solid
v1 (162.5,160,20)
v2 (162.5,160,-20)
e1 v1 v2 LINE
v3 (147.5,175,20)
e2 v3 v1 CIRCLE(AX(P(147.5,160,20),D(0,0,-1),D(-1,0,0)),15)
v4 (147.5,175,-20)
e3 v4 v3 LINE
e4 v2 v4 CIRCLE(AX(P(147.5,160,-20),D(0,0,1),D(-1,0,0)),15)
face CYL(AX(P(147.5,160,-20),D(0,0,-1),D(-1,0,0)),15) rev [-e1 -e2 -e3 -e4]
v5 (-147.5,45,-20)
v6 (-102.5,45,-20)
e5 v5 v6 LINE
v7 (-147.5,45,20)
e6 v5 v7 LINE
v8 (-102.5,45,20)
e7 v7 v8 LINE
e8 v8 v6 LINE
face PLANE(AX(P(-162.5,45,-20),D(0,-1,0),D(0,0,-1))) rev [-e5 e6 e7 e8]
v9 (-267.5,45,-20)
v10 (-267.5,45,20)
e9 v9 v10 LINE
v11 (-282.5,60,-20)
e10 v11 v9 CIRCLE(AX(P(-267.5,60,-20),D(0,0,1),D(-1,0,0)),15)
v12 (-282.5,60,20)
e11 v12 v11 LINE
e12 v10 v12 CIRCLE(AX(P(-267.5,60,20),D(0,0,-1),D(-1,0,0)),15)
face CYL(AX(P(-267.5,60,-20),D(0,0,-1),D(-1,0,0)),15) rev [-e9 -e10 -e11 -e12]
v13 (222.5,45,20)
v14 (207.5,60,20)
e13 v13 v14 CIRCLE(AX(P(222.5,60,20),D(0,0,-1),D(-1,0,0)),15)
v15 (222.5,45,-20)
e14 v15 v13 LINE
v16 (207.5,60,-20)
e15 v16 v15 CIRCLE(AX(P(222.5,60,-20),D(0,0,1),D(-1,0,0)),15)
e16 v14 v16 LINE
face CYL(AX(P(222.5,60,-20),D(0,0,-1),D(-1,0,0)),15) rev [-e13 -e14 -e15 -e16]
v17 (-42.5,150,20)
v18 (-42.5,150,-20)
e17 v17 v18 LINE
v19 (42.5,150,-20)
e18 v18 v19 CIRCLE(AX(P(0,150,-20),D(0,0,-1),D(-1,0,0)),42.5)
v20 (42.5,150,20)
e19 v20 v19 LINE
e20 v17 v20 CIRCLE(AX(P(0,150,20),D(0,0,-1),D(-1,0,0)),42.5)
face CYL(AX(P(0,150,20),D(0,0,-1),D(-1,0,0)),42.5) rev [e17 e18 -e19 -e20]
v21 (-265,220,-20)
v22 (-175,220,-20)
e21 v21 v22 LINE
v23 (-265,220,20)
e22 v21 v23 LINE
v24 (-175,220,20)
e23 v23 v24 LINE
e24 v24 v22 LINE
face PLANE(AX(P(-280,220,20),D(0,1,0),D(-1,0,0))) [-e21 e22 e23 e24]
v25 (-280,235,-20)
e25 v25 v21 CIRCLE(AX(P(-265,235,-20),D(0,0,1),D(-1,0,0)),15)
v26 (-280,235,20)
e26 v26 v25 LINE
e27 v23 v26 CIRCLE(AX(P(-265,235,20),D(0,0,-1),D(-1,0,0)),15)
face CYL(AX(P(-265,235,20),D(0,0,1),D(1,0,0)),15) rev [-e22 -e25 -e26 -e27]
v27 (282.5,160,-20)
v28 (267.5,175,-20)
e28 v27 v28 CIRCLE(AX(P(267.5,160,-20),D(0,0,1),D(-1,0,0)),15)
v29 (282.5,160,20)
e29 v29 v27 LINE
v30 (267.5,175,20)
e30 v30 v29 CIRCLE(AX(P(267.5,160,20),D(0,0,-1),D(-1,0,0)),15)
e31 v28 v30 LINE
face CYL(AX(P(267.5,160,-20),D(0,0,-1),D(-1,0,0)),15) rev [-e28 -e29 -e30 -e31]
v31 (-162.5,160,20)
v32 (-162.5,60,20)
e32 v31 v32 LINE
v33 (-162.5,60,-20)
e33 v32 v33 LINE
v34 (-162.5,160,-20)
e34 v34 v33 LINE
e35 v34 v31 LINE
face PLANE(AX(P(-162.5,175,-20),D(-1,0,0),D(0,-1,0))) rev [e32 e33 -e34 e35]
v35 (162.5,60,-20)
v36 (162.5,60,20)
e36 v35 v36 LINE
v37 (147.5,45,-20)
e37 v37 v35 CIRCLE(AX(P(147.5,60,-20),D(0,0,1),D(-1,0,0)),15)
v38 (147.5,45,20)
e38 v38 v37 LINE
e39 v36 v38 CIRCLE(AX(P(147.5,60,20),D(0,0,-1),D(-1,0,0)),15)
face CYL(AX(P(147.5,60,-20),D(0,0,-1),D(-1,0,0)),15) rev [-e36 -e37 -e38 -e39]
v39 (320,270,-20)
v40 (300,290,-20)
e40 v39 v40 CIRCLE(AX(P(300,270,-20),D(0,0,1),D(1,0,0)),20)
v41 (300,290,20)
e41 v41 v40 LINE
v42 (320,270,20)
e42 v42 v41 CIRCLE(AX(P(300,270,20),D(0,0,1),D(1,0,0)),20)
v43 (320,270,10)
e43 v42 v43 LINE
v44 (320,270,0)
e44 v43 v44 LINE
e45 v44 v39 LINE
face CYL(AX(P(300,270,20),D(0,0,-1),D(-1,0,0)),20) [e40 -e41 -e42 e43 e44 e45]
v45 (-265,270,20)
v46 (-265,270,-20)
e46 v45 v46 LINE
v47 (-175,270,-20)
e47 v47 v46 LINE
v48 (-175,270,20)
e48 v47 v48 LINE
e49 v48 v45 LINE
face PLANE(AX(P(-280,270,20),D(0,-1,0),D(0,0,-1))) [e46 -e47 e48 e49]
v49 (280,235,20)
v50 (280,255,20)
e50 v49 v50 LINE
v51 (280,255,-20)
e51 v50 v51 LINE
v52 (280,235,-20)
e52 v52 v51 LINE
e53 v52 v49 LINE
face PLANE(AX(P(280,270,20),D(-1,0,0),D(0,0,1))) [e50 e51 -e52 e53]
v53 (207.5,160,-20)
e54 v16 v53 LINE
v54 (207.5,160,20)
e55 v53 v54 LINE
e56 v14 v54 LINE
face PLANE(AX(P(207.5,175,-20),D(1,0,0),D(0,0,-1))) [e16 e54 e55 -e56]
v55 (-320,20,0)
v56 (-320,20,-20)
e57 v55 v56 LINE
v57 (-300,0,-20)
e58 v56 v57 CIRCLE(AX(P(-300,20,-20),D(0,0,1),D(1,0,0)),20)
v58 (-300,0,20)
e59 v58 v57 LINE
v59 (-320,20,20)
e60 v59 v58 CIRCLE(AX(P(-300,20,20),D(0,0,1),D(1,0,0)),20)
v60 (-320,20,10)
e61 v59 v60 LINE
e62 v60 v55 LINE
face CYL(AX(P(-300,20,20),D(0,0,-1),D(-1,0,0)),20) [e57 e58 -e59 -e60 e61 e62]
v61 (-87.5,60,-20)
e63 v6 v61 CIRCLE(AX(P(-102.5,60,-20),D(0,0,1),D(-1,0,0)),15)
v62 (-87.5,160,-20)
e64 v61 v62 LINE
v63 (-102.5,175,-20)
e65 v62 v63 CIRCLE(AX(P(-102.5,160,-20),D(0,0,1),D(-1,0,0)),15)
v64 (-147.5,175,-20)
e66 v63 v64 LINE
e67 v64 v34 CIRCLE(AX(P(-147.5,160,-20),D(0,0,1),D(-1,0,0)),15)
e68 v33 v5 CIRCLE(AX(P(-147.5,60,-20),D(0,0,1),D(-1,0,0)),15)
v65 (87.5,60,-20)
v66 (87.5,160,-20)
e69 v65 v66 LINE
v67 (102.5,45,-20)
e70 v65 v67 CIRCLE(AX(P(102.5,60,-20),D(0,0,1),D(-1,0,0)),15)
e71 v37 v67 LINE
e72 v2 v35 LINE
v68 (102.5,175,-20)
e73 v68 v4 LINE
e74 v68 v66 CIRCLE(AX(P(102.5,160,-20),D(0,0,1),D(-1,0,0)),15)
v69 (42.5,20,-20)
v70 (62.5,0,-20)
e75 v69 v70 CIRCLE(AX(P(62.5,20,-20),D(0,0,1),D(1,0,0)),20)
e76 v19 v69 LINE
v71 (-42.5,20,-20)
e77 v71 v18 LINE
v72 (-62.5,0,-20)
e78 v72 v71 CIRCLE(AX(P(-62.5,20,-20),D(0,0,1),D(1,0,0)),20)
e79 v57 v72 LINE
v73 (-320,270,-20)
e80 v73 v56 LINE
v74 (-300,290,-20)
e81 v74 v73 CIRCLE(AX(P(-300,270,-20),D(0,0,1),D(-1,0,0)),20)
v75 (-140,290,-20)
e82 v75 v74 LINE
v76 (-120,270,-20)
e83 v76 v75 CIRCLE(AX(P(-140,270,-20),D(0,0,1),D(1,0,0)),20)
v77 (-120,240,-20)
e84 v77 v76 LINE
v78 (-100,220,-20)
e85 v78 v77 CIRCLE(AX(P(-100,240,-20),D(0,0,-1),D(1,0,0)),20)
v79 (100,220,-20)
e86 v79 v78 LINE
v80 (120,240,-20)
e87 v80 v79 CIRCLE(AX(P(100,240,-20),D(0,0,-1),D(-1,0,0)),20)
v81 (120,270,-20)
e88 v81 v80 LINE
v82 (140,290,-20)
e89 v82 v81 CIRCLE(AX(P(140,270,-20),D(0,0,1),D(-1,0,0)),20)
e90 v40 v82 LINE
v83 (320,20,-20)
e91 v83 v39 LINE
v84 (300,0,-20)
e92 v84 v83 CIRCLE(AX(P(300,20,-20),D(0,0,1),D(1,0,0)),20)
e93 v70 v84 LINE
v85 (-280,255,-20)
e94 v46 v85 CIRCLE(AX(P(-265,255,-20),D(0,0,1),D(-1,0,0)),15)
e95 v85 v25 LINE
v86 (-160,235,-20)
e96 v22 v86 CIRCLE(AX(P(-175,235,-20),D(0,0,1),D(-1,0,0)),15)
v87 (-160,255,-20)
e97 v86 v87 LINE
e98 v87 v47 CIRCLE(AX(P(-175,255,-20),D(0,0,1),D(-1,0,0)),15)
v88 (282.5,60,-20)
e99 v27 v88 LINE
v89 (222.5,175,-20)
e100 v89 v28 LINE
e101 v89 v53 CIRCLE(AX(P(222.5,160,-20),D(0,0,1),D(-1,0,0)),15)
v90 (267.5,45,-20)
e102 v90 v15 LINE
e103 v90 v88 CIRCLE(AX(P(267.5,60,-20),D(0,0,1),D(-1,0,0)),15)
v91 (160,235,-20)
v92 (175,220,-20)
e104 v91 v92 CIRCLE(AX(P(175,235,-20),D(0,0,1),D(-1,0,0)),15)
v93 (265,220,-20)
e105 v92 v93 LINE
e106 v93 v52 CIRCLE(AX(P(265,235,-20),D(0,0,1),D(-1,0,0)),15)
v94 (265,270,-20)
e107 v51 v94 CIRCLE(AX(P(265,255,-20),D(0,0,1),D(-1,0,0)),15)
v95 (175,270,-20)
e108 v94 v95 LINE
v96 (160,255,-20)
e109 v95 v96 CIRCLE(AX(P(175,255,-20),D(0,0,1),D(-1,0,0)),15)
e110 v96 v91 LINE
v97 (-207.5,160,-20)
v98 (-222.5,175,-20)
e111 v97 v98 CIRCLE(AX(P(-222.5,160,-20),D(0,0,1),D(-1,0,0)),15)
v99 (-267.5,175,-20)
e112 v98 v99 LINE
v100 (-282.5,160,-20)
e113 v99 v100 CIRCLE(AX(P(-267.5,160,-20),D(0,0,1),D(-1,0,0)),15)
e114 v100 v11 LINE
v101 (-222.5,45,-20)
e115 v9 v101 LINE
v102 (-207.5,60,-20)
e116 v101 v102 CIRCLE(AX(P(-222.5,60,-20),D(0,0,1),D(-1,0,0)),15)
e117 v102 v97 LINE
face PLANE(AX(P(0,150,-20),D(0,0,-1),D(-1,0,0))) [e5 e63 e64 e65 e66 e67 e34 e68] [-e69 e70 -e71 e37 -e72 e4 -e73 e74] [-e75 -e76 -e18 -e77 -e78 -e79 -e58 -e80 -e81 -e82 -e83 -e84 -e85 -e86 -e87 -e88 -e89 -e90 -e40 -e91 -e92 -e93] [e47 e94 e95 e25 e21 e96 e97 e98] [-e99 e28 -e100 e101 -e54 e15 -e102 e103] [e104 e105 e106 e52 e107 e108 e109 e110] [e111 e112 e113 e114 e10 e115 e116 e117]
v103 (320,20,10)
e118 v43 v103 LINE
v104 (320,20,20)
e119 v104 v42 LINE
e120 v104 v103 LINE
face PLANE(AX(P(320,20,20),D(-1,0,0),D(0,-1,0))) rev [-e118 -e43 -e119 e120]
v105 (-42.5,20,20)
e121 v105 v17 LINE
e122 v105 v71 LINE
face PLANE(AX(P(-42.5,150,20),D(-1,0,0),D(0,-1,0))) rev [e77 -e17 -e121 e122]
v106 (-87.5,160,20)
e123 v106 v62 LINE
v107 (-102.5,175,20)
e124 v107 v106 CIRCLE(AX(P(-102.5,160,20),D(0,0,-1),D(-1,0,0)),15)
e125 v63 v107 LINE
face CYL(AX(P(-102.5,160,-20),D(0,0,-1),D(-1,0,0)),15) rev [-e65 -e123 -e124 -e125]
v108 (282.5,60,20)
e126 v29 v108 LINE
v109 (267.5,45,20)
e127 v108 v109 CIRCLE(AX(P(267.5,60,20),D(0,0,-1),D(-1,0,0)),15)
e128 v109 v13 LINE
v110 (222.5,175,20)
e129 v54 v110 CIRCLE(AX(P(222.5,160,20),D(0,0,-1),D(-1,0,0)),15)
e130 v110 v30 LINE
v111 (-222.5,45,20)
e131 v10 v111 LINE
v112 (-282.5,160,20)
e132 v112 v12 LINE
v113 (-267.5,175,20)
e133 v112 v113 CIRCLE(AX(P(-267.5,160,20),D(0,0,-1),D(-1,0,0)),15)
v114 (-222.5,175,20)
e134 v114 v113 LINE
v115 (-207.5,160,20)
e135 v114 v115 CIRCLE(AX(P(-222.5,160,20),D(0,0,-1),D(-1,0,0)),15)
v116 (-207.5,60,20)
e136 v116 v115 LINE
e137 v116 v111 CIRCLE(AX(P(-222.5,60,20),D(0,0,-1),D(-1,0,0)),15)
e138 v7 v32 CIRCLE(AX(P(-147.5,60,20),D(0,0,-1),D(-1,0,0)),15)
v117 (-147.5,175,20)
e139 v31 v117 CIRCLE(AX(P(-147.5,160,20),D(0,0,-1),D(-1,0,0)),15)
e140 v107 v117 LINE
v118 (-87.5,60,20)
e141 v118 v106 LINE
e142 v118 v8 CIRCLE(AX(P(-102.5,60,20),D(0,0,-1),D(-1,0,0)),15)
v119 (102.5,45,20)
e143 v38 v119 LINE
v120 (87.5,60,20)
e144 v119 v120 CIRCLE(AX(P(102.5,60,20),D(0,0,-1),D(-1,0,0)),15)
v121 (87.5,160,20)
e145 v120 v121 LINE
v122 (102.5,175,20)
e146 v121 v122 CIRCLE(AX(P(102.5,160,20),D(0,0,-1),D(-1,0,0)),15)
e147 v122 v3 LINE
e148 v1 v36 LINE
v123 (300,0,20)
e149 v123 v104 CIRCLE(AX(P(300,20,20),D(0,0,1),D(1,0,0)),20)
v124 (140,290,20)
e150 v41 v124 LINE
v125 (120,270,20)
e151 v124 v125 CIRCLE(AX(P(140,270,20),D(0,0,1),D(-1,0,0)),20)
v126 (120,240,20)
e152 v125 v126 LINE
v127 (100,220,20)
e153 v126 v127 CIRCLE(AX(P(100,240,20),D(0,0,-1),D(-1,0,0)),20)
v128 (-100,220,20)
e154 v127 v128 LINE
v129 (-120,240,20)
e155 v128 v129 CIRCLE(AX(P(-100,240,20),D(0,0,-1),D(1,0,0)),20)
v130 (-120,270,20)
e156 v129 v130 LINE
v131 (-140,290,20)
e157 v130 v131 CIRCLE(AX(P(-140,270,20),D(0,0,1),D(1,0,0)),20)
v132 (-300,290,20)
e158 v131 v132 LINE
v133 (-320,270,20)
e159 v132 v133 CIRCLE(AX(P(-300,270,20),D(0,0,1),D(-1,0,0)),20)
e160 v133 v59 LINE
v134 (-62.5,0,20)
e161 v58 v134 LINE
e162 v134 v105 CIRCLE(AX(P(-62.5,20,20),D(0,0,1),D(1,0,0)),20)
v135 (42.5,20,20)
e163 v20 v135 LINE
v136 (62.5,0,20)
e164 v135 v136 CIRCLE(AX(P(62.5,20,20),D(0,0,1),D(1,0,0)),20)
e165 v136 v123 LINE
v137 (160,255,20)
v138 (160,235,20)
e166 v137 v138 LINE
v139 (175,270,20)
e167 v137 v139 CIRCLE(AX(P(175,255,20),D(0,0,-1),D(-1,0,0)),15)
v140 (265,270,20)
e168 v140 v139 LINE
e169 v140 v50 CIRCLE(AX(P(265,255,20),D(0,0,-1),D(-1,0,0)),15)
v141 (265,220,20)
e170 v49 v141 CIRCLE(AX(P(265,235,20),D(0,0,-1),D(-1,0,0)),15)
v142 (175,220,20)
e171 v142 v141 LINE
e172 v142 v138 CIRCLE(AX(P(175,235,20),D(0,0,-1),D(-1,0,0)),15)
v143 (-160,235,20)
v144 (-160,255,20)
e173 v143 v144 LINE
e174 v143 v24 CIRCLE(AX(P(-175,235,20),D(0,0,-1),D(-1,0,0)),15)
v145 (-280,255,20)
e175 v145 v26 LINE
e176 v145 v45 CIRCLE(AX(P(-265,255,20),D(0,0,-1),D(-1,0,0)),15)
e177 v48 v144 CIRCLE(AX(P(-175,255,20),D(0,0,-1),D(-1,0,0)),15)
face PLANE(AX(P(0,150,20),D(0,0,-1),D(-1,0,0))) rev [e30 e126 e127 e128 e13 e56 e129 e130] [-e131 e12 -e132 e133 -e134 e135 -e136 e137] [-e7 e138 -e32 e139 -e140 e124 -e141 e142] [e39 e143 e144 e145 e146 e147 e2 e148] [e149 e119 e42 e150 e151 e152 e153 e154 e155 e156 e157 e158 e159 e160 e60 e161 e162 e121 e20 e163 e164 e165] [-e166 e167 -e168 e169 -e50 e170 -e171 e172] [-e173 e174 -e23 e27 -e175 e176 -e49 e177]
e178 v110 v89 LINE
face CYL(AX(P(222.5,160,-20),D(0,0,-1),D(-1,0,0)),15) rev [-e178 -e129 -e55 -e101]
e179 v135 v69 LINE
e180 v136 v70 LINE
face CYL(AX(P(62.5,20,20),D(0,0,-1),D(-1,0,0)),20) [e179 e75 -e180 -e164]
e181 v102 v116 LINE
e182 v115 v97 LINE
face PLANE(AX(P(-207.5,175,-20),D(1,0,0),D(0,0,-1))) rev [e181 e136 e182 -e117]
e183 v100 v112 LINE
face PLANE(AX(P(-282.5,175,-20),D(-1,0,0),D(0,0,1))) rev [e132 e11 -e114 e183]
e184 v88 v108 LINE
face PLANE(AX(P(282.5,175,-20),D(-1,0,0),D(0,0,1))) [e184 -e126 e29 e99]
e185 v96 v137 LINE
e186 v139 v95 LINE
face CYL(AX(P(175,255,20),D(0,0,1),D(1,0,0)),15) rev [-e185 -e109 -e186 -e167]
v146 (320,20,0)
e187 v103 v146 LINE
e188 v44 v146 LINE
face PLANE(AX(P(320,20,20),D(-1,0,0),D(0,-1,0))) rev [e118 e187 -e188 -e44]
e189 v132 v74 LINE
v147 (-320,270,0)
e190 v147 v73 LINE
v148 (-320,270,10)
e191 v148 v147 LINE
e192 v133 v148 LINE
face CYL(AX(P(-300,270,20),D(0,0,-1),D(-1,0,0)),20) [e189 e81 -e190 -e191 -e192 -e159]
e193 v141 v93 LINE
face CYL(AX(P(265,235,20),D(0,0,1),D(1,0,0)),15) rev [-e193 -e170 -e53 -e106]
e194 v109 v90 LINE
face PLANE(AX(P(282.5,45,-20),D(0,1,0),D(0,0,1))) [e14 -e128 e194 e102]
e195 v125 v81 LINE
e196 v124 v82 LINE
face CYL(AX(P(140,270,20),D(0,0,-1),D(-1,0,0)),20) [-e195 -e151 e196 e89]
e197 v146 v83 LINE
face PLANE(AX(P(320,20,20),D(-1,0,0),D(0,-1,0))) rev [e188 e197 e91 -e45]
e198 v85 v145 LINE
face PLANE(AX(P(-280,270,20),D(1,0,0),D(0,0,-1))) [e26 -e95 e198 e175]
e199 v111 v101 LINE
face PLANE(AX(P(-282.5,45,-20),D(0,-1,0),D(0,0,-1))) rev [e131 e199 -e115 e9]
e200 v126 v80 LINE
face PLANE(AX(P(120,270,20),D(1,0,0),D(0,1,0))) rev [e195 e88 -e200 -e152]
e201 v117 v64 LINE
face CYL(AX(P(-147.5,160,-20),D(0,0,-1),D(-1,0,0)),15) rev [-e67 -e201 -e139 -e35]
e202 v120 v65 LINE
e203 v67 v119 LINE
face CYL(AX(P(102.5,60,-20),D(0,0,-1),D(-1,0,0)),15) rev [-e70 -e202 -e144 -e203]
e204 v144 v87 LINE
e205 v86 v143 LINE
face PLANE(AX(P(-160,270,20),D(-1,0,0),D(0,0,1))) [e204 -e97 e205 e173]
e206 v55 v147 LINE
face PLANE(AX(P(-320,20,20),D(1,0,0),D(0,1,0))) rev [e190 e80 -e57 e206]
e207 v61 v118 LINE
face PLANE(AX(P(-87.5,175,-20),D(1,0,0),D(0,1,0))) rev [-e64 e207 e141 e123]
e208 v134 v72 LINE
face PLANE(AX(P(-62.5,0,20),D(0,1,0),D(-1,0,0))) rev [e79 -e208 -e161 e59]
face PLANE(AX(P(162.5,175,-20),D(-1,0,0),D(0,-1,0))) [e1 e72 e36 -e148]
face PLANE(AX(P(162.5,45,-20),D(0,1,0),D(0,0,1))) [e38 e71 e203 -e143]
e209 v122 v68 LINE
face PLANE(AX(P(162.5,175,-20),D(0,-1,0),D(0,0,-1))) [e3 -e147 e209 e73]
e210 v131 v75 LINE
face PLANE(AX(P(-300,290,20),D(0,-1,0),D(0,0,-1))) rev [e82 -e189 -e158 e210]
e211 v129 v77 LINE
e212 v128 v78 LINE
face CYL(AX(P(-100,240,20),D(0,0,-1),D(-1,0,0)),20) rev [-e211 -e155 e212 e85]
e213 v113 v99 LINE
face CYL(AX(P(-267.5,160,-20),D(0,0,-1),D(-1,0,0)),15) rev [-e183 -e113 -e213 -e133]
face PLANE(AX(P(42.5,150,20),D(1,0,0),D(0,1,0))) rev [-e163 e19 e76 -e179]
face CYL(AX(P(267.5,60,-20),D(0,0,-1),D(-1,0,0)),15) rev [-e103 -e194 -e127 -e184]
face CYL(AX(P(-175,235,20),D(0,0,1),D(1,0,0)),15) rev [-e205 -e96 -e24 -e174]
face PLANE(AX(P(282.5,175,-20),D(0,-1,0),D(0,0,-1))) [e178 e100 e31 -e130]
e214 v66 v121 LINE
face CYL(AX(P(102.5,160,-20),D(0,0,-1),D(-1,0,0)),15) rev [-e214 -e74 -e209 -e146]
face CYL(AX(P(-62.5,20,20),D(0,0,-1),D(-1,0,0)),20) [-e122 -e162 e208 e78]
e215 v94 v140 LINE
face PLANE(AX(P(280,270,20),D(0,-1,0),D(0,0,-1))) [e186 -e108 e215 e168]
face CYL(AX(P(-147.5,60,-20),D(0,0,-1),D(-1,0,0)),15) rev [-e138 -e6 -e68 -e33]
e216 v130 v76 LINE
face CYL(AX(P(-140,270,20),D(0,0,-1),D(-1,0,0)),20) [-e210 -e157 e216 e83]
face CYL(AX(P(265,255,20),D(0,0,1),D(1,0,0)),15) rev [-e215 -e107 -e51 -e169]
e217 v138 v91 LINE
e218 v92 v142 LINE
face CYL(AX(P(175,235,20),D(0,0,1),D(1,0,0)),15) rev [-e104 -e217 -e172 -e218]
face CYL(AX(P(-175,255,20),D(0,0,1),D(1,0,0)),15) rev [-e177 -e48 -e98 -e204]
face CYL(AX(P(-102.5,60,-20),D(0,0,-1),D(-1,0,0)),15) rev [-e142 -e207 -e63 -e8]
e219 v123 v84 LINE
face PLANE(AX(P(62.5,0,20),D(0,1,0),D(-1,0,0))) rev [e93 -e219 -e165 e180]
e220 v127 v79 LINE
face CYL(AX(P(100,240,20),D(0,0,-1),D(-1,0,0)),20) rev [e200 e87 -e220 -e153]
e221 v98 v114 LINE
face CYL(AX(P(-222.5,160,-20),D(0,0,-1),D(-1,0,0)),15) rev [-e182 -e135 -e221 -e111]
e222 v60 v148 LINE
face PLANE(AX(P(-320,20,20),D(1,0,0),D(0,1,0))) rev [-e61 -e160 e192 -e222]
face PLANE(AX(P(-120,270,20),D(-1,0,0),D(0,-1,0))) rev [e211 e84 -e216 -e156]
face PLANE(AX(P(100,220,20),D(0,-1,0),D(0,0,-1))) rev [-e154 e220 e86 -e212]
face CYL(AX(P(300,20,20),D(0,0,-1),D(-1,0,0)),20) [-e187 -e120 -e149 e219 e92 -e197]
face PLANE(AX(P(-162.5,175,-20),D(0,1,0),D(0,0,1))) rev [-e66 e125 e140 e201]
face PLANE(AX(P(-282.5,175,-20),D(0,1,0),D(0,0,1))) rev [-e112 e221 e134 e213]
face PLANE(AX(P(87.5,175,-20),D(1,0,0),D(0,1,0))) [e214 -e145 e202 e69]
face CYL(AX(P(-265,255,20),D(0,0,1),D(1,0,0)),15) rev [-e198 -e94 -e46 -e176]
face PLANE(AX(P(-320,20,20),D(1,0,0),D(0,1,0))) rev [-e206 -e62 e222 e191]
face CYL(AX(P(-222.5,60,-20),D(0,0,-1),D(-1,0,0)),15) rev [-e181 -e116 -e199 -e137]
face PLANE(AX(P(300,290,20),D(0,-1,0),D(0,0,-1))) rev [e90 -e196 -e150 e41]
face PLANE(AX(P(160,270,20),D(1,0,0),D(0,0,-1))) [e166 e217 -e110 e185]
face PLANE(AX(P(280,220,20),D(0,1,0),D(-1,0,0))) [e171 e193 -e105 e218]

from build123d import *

# Parameters (mm, degrees)
SKETCH1_W            = 120
SKETCH1_H            = 50
BOSS_EXTRUDE1_DEPTH  = 20
FILLET1_R            = 15
SKETCH2_W            = 75
SKETCH2_H            = 130
CUT_EXTRUDE1_DEPTH   = 433.319326424
FILLET2_R            = 15
FILLET2_OF_MIRROR1_R = 15


with BuildPart() as part:
    # Sketch1 → Boss-Extrude1 (new, symmetric)
    with BuildSketch(Plane.XY):
        with BuildLine():
            Line((42.5, 150), (42.5, 20))
            ThreePointArc((42.5, 20), (48.357864376, 5.857864376), (62.5, 0))
            Line((62.5, 0), (300, 0))
            ThreePointArc((300, 0), (314.142135624, 5.857864376), (320, 20))
            Line((320, 20), (320, 270))
            ThreePointArc((320, 270), (314.142135624, 284.142135624), (300, 290))
            Line((300, 290), (140, 290))
            ThreePointArc((140, 290), (125.857864376, 284.142135624), (120, 270))
            Line((120, 270), (120, 240))
            ThreePointArc((120, 240), (114.142135624, 225.857864376), (100, 220))
            Line((100, 220), (-100, 220))
            ThreePointArc((-100, 220), (-114.142135624, 225.857864376), (-120, 240))
            Line((-120, 240), (-120, 270))
            ThreePointArc((-120, 270), (-125.857864376, 284.142135624), (-140, 290))
            Line((-140, 290), (-300, 290))
            ThreePointArc((-300, 290), (-314.142135624, 284.142135624), (-320, 270))
            Line((-320, 270), (-320, 20))
            ThreePointArc((-320, 20), (-314.142135624, 5.857864376), (-300, 0))
            Line((-300, 0), (-62.5, 0))
            ThreePointArc((-62.5, 0), (-48.357864376, 5.857864376), (-42.5, 20))
            Line((-42.5, 20), (-42.5, 150))
            ThreePointArc((-42.5, 150), (0, 192.5), (42.5, 150))
        make_face()
        with Locations((-220, 245)):
            Rectangle(SKETCH1_W, SKETCH1_H, mode=Mode.SUBTRACT)
        with Locations((220, 245)):
            Rectangle(SKETCH1_W, SKETCH1_H, mode=Mode.SUBTRACT)
    extrude(amount=BOSS_EXTRUDE1_DEPTH, both=True)

    # Fillet1
    fillet1_edges = [part.edges().sort_by_distance(p)[0] for p in [
        (-160, 220, 0),
        (-160, 270, 0),
        (-280, 270, 0),
        (-280, 220, 0),
        (280, 220, 0),
        (280, 270, 0),
        (160, 270, 0),
        (160, 220, 0),
    ]]
    fillet(fillet1_edges, radius=FILLET1_R)

    # Sketch2 → Cut-Extrude1 (cut, symmetric)
    with BuildSketch(Plane.XY):
        with Locations((-245, 110)):
            Rectangle(SKETCH2_W, SKETCH2_H)
        with Locations((-125, 110)):
            Rectangle(SKETCH2_W, SKETCH2_H)
    cut_extrude1 = extrude(amount=CUT_EXTRUDE1_DEPTH, both=True, mode=Mode.SUBTRACT)

    # Fillet2
    fillet2_edges = [part.edges().sort_by_distance(p)[0] for p in [
        (-207.5, 175, 0),
        (-207.5, 45, 0),
        (-282.5, 45, 0),
        (-282.5, 175, 0),
        (-87.5, 175, 0),
        (-87.5, 45, 0),
        (-162.5, 45, 0),
        (-162.5, 175, 0),
    ]]
    fillet(fillet2_edges, radius=FILLET2_R)

    # Mirror1: Cut-Extrude1 across plane
    add(cut_extrude1.mirror(Plane(origin=(0, 0, 0), x_dir=(0, 0, 1), z_dir=(1, 0, 0))), mode=Mode.SUBTRACT)

    # Fillet2 of Mirror1
    fillet2_of_mirror1_edges = [part.edges().sort_by_distance(p)[0] for p in [
        (207.5, 175, 0),
        (207.5, 45, 0),
        (282.5, 45, 0),
        (282.5, 175, 0),
        (87.5, 175, 0),
        (87.5, 45, 0),
        (162.5, 45, 0),
        (162.5, 175, 0),
    ]]
    fillet(fillet2_of_mirror1_edges, radius=FILLET2_OF_MIRROR1_R)


solid = part.part
